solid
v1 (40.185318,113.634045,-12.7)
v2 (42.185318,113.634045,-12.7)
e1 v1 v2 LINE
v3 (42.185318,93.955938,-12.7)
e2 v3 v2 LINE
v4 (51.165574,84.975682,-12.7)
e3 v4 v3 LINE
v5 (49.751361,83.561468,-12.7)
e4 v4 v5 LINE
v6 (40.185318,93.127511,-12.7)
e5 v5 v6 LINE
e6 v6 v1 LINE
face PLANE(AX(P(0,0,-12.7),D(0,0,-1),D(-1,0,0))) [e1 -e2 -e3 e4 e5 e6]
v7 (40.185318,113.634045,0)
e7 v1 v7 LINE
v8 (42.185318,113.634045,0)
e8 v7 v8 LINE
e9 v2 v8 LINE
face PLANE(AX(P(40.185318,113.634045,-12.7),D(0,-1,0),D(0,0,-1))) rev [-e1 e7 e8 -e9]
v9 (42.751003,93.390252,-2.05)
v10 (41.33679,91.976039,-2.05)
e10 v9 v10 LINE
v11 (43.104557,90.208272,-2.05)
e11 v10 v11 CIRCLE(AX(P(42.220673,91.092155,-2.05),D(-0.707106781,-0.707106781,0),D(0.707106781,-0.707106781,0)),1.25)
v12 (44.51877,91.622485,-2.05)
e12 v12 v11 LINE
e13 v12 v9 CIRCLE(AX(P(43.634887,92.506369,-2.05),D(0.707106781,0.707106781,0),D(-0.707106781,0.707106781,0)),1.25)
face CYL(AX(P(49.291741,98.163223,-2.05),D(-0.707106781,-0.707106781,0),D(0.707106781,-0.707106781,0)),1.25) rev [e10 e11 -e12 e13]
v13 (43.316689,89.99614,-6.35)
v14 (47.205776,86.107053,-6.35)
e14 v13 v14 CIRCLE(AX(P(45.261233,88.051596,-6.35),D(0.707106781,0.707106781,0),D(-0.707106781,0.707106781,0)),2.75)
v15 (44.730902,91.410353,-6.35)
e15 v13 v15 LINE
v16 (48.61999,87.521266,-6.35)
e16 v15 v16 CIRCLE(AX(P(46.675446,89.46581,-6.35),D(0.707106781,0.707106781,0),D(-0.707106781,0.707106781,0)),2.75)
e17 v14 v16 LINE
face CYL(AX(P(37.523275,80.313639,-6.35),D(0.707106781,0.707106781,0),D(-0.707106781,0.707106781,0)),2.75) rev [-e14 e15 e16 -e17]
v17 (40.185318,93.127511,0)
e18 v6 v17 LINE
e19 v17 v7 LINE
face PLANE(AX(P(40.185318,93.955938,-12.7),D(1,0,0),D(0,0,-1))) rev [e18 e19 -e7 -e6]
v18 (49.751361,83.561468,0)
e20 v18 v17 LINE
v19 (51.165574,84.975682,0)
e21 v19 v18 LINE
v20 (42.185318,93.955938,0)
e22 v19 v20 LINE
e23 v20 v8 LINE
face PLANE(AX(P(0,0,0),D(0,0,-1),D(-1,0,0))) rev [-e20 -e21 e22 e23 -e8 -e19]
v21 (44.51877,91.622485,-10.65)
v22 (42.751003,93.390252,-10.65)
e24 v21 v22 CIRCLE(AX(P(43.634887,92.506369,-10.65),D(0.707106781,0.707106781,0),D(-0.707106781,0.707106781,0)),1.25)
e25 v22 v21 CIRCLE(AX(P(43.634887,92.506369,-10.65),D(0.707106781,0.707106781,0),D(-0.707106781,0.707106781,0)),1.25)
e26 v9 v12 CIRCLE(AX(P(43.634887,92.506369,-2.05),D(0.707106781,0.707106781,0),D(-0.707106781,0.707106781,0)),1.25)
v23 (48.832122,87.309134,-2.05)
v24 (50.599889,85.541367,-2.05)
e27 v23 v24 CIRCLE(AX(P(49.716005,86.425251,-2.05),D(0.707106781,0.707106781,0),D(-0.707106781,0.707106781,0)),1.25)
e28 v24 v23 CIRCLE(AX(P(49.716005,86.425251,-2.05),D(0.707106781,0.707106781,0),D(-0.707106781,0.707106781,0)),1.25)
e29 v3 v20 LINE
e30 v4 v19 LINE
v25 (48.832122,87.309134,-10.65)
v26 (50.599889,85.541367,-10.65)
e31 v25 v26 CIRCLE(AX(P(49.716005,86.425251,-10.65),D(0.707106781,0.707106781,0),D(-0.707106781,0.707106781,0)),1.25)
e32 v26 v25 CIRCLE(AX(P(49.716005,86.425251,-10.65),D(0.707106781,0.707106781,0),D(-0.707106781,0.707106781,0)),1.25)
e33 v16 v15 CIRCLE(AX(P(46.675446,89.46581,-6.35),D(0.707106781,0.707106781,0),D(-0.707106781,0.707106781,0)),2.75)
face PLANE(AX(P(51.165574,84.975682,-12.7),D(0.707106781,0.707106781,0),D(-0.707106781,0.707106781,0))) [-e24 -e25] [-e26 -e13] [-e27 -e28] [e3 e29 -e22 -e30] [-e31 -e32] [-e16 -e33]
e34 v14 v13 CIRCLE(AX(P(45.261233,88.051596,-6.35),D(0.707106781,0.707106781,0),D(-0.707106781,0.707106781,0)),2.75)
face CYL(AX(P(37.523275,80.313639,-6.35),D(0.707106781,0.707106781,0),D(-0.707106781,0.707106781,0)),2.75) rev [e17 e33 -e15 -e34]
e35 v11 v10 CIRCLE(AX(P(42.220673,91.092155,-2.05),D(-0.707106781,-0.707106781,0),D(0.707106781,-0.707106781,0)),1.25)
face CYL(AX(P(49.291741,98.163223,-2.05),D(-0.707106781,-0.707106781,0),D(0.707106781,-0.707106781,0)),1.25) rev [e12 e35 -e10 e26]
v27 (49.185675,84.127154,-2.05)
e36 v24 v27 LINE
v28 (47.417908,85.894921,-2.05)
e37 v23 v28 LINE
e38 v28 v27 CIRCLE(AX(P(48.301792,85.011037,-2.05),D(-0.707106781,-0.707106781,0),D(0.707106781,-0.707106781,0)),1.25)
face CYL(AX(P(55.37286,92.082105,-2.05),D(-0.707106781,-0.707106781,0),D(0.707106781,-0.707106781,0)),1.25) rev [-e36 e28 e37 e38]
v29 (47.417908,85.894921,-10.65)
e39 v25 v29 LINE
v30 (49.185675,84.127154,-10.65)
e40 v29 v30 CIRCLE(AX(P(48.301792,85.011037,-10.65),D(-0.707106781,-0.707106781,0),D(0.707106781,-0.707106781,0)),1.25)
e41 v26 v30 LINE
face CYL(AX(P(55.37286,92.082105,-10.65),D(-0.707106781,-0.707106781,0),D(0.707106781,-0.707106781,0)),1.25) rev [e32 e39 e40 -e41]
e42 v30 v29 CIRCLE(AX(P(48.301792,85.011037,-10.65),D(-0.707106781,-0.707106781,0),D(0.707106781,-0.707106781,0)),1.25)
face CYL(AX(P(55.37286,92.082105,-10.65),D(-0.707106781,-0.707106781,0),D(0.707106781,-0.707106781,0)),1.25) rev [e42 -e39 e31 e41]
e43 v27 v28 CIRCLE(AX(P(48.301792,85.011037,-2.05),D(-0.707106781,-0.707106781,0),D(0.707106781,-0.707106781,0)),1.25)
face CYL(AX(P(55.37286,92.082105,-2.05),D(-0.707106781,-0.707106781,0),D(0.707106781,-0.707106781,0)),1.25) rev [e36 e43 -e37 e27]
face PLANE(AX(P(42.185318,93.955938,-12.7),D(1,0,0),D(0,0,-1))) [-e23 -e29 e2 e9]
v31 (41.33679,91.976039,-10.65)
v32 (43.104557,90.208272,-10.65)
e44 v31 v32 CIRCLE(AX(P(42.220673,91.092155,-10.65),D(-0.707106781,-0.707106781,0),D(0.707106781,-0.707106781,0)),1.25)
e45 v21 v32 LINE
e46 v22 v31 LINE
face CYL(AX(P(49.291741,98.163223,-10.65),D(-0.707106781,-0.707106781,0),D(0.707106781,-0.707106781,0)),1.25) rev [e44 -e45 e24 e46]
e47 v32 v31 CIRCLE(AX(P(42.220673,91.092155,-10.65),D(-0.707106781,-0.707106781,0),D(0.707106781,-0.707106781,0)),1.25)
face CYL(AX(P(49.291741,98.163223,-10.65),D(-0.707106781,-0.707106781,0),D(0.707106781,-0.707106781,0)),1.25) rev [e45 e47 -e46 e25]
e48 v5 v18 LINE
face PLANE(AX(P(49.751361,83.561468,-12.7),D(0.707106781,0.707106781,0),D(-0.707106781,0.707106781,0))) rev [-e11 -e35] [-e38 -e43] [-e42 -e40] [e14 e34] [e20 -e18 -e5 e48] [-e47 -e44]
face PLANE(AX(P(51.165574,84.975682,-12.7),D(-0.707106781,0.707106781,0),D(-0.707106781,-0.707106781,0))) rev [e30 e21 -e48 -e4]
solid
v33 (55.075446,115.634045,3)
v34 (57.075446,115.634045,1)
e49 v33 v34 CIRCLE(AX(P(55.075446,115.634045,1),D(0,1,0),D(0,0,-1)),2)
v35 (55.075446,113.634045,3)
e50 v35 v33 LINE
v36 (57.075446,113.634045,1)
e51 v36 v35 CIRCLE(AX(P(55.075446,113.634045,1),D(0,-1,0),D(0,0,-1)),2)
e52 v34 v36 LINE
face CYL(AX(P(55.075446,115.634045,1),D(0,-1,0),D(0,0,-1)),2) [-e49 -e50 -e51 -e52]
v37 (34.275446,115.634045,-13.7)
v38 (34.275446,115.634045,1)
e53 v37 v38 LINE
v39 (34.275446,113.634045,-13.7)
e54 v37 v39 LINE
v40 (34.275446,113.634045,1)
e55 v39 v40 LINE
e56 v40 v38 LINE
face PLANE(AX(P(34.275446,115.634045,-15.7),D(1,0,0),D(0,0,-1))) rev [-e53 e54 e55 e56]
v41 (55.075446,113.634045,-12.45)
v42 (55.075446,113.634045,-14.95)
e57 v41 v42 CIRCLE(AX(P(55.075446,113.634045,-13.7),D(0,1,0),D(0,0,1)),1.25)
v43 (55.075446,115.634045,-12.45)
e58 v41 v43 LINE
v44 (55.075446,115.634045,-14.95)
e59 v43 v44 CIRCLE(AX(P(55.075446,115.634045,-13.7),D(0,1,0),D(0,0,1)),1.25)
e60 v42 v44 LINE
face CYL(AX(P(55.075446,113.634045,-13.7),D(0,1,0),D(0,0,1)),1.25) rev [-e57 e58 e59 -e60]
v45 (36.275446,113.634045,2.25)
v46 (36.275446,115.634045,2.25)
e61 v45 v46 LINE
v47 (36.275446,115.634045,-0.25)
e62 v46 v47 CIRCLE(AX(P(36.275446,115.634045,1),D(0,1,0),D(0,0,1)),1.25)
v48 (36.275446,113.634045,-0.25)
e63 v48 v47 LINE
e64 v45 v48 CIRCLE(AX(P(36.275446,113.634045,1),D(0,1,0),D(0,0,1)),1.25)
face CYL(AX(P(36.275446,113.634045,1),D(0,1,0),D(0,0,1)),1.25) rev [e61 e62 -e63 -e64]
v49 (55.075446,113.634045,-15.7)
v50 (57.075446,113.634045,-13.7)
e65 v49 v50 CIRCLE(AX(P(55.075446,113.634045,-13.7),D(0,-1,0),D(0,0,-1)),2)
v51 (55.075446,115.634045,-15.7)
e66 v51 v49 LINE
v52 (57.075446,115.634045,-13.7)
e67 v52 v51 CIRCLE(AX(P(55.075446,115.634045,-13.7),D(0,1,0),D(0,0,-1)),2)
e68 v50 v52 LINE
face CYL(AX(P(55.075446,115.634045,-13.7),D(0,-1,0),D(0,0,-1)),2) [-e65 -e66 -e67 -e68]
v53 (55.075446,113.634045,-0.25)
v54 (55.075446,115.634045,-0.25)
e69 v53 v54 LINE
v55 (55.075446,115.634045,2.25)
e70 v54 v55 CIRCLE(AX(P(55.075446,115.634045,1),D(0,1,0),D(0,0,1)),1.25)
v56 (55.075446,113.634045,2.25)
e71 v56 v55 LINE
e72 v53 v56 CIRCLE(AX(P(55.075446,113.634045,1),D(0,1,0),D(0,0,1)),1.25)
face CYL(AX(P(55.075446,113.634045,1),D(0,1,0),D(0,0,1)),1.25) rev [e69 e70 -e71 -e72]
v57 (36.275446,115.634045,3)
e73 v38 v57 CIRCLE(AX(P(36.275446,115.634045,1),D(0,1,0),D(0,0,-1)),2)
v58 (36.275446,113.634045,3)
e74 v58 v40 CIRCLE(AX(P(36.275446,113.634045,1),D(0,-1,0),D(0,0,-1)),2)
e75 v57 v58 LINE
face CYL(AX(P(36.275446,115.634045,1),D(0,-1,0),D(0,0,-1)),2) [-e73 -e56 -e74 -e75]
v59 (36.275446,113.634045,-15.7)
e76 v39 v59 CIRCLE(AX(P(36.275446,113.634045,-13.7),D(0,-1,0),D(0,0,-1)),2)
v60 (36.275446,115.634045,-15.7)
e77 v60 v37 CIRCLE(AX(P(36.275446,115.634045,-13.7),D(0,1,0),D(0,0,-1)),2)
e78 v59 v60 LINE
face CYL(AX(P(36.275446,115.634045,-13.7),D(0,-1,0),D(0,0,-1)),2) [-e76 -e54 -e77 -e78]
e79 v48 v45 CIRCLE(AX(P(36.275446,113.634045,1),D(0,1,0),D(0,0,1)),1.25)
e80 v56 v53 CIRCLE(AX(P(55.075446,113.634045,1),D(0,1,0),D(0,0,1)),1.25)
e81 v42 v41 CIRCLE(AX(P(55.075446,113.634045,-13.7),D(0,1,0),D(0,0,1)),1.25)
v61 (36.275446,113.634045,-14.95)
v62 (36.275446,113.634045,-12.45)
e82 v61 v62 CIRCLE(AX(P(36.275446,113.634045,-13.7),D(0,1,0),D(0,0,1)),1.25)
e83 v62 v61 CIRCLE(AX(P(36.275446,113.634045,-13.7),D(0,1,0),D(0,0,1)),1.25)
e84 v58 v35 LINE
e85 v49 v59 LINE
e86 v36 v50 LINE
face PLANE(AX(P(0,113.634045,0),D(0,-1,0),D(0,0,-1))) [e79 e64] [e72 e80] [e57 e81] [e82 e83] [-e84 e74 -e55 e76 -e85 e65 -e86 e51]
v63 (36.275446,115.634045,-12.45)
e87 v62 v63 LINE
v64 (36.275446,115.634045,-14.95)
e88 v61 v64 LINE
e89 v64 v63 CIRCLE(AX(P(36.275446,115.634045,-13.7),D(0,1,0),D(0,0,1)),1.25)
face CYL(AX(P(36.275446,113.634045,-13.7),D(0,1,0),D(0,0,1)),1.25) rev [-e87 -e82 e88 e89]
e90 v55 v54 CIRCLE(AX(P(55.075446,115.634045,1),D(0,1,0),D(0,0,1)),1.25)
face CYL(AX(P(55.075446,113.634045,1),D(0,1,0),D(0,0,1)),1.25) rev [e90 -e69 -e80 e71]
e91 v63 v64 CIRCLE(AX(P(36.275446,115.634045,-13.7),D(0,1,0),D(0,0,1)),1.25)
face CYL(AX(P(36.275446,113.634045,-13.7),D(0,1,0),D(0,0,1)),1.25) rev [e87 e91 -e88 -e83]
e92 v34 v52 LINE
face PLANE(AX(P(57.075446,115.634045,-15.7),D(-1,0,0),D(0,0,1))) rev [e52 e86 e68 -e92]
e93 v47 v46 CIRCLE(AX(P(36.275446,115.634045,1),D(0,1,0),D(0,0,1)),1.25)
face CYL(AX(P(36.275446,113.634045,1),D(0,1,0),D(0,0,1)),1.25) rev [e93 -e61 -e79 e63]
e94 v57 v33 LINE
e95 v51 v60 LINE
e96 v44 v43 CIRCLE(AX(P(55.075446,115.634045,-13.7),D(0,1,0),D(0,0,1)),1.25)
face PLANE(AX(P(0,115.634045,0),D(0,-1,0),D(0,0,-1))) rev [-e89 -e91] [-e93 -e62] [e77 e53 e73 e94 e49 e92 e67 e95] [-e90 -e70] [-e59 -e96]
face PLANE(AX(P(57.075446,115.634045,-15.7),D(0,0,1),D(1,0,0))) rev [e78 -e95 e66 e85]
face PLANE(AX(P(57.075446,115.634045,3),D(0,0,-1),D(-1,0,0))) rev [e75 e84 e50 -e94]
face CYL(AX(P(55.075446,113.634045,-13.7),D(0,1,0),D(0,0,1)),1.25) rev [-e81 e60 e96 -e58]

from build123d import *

# Parameters (mm, degrees)
EXTRUDE_THIN1_DEPTH     = 12.7
SKETCH3_W               = 22.8
SKETCH3_H               = 18.7
BOSS_EXTRUDE2_DEPTH     = 2
FILLET1_R               = 2
SKETCH4_R               = 1.25
CUT_EXTRUDE1_DEPTH      = 2
CUT_EXTRUDE2_DEPTH      = 61.42253709
CUT_EXTRUDE2_DEPTH_BACK = 61.42253709
SKETCH5_R               = 2.75
SKETCH6_R               = 1.25
CUT_EXTRUDE3_DEPTH      = 10


with BuildPart() as part:
    # Sketch1 → Extrude-Thin1 (new body)
    with BuildSketch(Plane.XY):
        Polygon((51.165574182, 84.975681723), (42.185318061, 93.955937844), (42.185318061, 113.634045339), (40.185318061, 113.634045339), (40.185318061, 93.127510719), (49.75136062, 83.561468161), align=None)
    extrude(amount=-EXTRUDE_THIN1_DEPTH)

    # Sketch5 → Cut-Extrude2 (cut, two sides: drawn at the far end of the back side and taken through both)
    with BuildSketch(Plane(origin=(68.070627953, 68.070627953, 0), x_dir=(0, 0, -1), z_dir=(0.7071067811865513, 0.7071067811865437, 0)).offset(-CUT_EXTRUDE2_DEPTH_BACK)):
        with Locations(Location((6.35, 30.257356315, 0), (0, 0, 90))):
            Circle(SKETCH5_R)
    extrude(amount=CUT_EXTRUDE2_DEPTH + CUT_EXTRUDE2_DEPTH_BACK, mode=Mode.SUBTRACT)

    # Sketch6 → Cut-Extrude3 (cut)
    with BuildSketch(Plane(origin=(66.65641439, 66.65641439, 0), x_dir=(0, 0, 1), z_dir=(-0.7071067811865513, -0.7071067811865437, 0))):
        with Locations(Location((-10.65, 34.557356315, 0), (0, 0, 270))):
            Circle(SKETCH6_R)
        with Locations(Location((-2.05, 34.557356315, 0), (0, 0, 270))):
            Circle(SKETCH6_R)
        with Locations(Location((-2.05, 25.957356315, 0), (0, 0, 270))):
            Circle(SKETCH6_R)
        with Locations(Location((-10.65, 25.957356315, 0), (0, 0, 270))):
            Circle(SKETCH6_R)
    extrude(amount=-CUT_EXTRUDE3_DEPTH, mode=Mode.SUBTRACT)


with BuildPart() as body_2:
    # Sketch3 → Boss-Extrude2 (new body)
    with BuildSketch(Plane(origin=(0, 113.634045339, 0), x_dir=(1, 0, 0), z_dir=(0, 1, 0))):
        with Locations((45.675446122, 6.35)):
            Rectangle(SKETCH3_W, SKETCH3_H)
    extrude(amount=BOSS_EXTRUDE2_DEPTH)

    # Fillet1
    fillet1_edges = [body_2.edges().sort_by_distance(p)[0] for p in [
        (57.075446122, 114.634045339, 3),
        (34.275446122, 114.634045339, 3),
        (34.275446122, 114.634045339, -15.7),
        (57.075446122, 114.634045339, -15.7),
    ]]
    fillet(fillet1_edges, radius=FILLET1_R)

    # Sketch4 → Cut-Extrude1 (cut)
    with BuildSketch(Plane(origin=(0, 115.634045339, 0), x_dir=(1, 0, 0), z_dir=(0, 1, 0))):
        with Locations(Location((55.075446122, 13.7, 0), (0, 0, 270))):
            Circle(SKETCH4_R)
        with Locations(Location((55.075446122, -1, 0), (0, 0, 270))):
            Circle(SKETCH4_R)
        with Locations(Location((36.275446122, -1, 0), (0, 0, 270))):
            Circle(SKETCH4_R)
        with Locations(Location((36.275446122, 13.7, 0), (0, 0, 270))):
            Circle(SKETCH4_R)
    extrude(amount=-CUT_EXTRUDE1_DEPTH, mode=Mode.SUBTRACT)


solid = Compound([part.part, body_2.part])
